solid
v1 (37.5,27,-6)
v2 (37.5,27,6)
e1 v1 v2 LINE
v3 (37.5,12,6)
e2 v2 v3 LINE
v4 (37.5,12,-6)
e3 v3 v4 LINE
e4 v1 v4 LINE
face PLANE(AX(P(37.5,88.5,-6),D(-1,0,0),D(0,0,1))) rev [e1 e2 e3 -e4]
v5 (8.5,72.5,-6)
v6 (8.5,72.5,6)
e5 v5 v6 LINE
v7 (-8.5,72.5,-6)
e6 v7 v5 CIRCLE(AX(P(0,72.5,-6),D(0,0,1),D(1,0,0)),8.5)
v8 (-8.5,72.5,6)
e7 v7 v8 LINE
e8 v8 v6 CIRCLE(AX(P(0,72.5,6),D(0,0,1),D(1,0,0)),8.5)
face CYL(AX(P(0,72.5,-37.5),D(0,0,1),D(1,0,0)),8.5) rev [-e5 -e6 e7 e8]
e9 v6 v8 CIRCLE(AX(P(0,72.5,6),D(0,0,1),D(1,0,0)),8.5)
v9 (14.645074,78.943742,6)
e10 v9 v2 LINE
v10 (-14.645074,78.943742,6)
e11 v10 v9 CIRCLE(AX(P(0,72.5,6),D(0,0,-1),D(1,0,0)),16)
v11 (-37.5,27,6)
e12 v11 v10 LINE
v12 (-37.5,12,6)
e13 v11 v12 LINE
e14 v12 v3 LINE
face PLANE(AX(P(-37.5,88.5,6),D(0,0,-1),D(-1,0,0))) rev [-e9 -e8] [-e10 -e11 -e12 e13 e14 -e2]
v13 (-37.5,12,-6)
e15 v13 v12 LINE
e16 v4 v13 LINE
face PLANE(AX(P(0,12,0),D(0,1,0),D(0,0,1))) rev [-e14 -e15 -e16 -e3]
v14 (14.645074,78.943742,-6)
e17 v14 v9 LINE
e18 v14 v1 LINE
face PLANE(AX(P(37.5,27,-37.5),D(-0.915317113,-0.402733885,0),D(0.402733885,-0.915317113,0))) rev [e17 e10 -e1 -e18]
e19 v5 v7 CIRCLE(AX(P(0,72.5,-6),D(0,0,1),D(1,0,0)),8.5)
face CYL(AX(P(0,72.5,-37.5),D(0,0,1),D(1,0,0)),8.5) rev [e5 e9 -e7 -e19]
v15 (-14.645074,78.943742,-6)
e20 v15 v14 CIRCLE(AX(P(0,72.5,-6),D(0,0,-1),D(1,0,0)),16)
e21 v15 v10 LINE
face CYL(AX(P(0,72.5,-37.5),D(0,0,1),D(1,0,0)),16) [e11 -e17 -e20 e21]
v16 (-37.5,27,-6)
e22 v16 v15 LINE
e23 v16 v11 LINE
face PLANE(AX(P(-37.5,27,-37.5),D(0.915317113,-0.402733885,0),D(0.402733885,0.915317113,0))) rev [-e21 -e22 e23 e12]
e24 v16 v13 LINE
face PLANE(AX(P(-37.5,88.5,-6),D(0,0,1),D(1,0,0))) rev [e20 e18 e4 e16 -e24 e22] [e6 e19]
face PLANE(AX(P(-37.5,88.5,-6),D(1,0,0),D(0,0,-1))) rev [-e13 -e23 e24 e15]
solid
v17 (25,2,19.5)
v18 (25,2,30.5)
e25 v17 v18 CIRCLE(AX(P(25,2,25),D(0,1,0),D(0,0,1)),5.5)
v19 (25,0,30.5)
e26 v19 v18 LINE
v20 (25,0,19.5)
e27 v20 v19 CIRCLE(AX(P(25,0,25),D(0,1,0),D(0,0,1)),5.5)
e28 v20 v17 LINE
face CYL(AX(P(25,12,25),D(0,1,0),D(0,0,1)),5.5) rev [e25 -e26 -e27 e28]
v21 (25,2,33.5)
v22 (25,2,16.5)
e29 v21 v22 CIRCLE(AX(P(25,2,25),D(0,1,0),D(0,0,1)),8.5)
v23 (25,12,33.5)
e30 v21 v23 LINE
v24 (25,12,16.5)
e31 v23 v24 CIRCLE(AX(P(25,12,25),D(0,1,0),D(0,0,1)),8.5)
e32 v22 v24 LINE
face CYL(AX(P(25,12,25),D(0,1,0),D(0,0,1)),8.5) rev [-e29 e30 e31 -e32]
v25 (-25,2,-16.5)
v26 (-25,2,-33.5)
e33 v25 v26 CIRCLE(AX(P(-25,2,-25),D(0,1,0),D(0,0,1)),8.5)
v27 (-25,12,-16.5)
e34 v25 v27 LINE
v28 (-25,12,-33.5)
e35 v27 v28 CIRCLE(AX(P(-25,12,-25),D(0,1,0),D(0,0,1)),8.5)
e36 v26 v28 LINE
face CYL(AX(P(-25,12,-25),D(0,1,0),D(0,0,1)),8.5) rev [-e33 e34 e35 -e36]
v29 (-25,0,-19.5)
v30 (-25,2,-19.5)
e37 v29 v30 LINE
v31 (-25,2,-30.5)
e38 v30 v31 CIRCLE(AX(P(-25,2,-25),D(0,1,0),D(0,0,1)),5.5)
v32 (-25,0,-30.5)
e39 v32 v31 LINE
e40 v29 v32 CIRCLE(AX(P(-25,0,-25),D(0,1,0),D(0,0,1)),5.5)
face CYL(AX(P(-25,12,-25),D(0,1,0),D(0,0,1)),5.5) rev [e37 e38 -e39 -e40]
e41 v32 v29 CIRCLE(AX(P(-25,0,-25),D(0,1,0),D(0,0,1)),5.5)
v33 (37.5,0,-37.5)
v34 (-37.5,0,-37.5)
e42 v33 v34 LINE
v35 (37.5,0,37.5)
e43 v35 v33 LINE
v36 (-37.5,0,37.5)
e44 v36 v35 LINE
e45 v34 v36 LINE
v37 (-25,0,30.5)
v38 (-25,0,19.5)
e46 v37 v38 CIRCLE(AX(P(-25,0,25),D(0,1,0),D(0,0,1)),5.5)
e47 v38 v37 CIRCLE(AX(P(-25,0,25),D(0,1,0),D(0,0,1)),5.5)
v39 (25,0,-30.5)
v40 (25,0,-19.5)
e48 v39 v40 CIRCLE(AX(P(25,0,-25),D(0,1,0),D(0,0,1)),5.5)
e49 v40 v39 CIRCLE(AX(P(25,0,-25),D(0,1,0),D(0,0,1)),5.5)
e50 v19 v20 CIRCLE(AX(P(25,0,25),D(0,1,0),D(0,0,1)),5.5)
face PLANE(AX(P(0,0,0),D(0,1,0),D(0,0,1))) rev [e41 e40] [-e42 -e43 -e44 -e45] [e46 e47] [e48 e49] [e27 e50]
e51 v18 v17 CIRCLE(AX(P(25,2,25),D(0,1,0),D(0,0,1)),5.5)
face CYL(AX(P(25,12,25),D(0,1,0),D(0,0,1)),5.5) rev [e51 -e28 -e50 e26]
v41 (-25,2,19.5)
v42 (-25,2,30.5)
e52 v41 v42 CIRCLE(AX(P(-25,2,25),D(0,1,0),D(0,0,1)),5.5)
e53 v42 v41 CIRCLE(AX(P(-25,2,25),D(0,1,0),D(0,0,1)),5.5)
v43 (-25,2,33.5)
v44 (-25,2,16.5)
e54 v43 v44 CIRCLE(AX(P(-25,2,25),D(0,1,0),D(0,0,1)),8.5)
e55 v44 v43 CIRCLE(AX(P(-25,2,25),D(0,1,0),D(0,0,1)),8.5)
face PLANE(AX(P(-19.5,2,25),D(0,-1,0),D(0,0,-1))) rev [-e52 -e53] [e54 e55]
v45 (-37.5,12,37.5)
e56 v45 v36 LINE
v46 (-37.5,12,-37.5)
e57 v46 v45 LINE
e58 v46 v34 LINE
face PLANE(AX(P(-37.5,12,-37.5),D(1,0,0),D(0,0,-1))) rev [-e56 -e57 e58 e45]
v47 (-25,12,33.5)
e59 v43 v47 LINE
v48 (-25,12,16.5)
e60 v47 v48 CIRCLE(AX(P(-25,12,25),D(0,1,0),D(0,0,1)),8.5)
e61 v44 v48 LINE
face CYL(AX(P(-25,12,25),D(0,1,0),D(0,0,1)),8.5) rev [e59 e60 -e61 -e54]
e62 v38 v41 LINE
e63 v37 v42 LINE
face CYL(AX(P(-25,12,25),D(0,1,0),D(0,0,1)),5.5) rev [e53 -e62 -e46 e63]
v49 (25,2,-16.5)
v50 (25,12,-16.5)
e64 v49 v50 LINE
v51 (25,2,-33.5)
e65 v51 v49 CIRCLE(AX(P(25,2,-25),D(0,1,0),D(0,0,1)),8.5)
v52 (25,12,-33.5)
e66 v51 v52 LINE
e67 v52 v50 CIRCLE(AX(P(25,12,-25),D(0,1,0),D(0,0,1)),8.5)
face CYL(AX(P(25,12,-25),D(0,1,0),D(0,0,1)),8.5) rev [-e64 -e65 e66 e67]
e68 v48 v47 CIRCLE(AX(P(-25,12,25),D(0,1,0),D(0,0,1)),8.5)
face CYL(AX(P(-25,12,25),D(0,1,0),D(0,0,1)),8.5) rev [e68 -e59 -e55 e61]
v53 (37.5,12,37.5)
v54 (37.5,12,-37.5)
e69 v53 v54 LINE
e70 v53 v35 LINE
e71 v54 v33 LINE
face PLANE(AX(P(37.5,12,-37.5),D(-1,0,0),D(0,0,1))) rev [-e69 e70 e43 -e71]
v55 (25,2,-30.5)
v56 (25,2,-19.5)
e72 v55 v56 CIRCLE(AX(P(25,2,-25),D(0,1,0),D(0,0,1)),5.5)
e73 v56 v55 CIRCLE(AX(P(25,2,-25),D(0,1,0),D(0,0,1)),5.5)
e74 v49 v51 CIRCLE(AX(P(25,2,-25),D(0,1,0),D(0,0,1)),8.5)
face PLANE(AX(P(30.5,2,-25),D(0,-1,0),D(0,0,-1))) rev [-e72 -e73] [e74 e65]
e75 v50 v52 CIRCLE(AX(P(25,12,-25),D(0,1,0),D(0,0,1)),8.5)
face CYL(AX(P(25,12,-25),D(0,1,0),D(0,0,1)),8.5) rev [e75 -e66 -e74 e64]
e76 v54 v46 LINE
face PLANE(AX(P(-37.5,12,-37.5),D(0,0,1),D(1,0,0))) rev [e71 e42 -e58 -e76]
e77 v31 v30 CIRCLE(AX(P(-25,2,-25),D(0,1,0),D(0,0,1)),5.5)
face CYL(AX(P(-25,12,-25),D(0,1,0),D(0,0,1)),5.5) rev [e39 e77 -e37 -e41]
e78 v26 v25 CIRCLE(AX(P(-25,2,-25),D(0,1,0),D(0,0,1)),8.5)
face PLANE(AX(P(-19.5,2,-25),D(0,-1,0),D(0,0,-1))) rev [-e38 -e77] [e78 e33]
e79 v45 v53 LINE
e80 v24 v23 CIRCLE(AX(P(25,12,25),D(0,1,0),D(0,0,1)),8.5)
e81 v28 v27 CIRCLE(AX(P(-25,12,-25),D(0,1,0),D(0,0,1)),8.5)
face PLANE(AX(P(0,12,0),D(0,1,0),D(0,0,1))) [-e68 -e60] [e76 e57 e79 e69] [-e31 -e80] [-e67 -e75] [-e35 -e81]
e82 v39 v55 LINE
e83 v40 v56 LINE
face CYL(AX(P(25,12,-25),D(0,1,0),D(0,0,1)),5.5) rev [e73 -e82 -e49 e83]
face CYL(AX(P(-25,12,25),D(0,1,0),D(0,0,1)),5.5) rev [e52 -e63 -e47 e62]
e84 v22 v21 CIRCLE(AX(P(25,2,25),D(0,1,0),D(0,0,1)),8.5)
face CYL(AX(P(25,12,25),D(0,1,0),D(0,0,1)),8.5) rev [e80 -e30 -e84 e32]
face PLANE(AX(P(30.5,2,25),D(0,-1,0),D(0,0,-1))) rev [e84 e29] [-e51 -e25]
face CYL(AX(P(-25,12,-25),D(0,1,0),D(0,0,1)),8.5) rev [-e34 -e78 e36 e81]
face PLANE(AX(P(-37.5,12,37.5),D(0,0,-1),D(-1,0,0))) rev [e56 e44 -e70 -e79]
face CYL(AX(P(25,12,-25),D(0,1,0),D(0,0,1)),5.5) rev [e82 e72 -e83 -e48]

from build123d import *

# Parameters (mm, degrees)
SKETCH1_W                               = 75
SKETCH1_H                               = 75
BOSS_EXTRUDE1_DEPTH                     = 12
SKETCH2_W                               = 75
SKETCH2_H                               = 12
BOSS_EXTRUDE2_DEPTH                     = 76.5
SKETCH3_R                               = 8.5
CUT_EXTRUDE1_DEPTH                      = 106.502369642
CUT_EXTRUDE2_DEPTH                      = 106.502369642
CBORE_FOR_M10_HEX_HEAD_BOLT2_AT_2_COUNT = 2
CBORE_FOR_M10_HEX_HEAD_BOLT2_AT_2_PITCH = 70.710678119
CBORE_FOR_M10_HEX_HEAD_BOLT2_AT_3_COUNT = 2
CBORE_FOR_M10_HEX_HEAD_BOLT2_AT_3_PITCH = 50
CBORE_FOR_M10_HEX_HEAD_BOLT2_AT_4_COUNT = 2
CBORE_FOR_M10_HEX_HEAD_BOLT2_AT_4_PITCH = 50


with BuildPart() as part:
    # Sketch1 → Boss-Extrude1 (new body)
    with BuildSketch(Plane(origin=(0, 0, 0), x_dir=(1, 0, 0), z_dir=(0, 1, 0))):
        Rectangle(SKETCH1_W, SKETCH1_H)
    extrude(amount=BOSS_EXTRUDE1_DEPTH)

    # Sketch6 → CBORE for M10 Hex Head Bolt2 (revolve, cut)
    with BuildSketch(Plane(origin=(25, 12, 25), x_dir=(0, 0, 1), z_dir=(1, 0, 0))):
        Polygon((0, 0), (0, 46.804733405), (5.5, 43.5), (5.5, 10), (8.5, 10), (8.5, 0), align=None)
    cbore_for_m10_hex_head_bolt2 = revolve(axis=Axis((25, 18.35, 25), (0, -1, 0)), mode=Mode.SUBTRACT)

    # CBORE for M10 Hex Head Bolt2 at 2: CBORE for M10 Hex Head Bolt2 ×2
    with Locations(*[Vector(-0.7071067811865476, 0, -0.7071067811865475) * (i * CBORE_FOR_M10_HEX_HEAD_BOLT2_AT_2_PITCH) for i in range(1, CBORE_FOR_M10_HEX_HEAD_BOLT2_AT_2_COUNT)]):
        add(cbore_for_m10_hex_head_bolt2, mode=Mode.SUBTRACT)

    # CBORE for M10 Hex Head Bolt2 at 3: CBORE for M10 Hex Head Bolt2 ×2
    with Locations(*[(-i * CBORE_FOR_M10_HEX_HEAD_BOLT2_AT_3_PITCH, 0, 0) for i in range(1, CBORE_FOR_M10_HEX_HEAD_BOLT2_AT_3_COUNT)]):
        add(cbore_for_m10_hex_head_bolt2, mode=Mode.SUBTRACT)

    # CBORE for M10 Hex Head Bolt2 at 4: CBORE for M10 Hex Head Bolt2 ×2
    with Locations(*[(0, 0, -i * CBORE_FOR_M10_HEX_HEAD_BOLT2_AT_4_PITCH) for i in range(1, CBORE_FOR_M10_HEX_HEAD_BOLT2_AT_4_COUNT)]):
        add(cbore_for_m10_hex_head_bolt2, mode=Mode.SUBTRACT)


with BuildPart() as body_2:
    # Sketch2 → Boss-Extrude2 (new body)
    with BuildSketch(Plane(origin=(0, 12, 0), x_dir=(1, 0, 0), z_dir=(0, 1, 0))):
        Rectangle(SKETCH2_W, SKETCH2_H)
    extrude(amount=BOSS_EXTRUDE2_DEPTH)

    # Sketch3 → Cut-Extrude1 (cut, through all)
    with BuildSketch(Plane.XY.offset(6)):
        with Locations((0, 72.5)):
            Circle(SKETCH3_R)
    extrude(amount=-CUT_EXTRUDE1_DEPTH, mode=Mode.SUBTRACT)

    # Sketch4 → Cut-Extrude2 (cut, through all)
    with BuildSketch(Plane.XY.offset(6)):
        with BuildLine():
            Line((-37.5, 27), (-14.645073815, 78.943742155))
            ThreePointArc((-14.645073815, 78.943742155), (0, 88.5), (14.645073815, 78.943742155))
            Line((14.645073815, 78.943742155), (37.5, 27))
            Line((37.5, 27), (37.5, 88.5))
            Line((37.5, 88.5), (37.5, 96.342049546))
            Line((37.5, 96.342049546), (-37.5, 96.342049546))
            Line((-37.5, 96.342049546), (-37.5, 88.5))
            Line((-37.5, 88.5), (-37.5, 27))
        make_face()
    extrude(amount=-CUT_EXTRUDE2_DEPTH, mode=Mode.SUBTRACT)


solid = Compound([part.part, body_2.part])
